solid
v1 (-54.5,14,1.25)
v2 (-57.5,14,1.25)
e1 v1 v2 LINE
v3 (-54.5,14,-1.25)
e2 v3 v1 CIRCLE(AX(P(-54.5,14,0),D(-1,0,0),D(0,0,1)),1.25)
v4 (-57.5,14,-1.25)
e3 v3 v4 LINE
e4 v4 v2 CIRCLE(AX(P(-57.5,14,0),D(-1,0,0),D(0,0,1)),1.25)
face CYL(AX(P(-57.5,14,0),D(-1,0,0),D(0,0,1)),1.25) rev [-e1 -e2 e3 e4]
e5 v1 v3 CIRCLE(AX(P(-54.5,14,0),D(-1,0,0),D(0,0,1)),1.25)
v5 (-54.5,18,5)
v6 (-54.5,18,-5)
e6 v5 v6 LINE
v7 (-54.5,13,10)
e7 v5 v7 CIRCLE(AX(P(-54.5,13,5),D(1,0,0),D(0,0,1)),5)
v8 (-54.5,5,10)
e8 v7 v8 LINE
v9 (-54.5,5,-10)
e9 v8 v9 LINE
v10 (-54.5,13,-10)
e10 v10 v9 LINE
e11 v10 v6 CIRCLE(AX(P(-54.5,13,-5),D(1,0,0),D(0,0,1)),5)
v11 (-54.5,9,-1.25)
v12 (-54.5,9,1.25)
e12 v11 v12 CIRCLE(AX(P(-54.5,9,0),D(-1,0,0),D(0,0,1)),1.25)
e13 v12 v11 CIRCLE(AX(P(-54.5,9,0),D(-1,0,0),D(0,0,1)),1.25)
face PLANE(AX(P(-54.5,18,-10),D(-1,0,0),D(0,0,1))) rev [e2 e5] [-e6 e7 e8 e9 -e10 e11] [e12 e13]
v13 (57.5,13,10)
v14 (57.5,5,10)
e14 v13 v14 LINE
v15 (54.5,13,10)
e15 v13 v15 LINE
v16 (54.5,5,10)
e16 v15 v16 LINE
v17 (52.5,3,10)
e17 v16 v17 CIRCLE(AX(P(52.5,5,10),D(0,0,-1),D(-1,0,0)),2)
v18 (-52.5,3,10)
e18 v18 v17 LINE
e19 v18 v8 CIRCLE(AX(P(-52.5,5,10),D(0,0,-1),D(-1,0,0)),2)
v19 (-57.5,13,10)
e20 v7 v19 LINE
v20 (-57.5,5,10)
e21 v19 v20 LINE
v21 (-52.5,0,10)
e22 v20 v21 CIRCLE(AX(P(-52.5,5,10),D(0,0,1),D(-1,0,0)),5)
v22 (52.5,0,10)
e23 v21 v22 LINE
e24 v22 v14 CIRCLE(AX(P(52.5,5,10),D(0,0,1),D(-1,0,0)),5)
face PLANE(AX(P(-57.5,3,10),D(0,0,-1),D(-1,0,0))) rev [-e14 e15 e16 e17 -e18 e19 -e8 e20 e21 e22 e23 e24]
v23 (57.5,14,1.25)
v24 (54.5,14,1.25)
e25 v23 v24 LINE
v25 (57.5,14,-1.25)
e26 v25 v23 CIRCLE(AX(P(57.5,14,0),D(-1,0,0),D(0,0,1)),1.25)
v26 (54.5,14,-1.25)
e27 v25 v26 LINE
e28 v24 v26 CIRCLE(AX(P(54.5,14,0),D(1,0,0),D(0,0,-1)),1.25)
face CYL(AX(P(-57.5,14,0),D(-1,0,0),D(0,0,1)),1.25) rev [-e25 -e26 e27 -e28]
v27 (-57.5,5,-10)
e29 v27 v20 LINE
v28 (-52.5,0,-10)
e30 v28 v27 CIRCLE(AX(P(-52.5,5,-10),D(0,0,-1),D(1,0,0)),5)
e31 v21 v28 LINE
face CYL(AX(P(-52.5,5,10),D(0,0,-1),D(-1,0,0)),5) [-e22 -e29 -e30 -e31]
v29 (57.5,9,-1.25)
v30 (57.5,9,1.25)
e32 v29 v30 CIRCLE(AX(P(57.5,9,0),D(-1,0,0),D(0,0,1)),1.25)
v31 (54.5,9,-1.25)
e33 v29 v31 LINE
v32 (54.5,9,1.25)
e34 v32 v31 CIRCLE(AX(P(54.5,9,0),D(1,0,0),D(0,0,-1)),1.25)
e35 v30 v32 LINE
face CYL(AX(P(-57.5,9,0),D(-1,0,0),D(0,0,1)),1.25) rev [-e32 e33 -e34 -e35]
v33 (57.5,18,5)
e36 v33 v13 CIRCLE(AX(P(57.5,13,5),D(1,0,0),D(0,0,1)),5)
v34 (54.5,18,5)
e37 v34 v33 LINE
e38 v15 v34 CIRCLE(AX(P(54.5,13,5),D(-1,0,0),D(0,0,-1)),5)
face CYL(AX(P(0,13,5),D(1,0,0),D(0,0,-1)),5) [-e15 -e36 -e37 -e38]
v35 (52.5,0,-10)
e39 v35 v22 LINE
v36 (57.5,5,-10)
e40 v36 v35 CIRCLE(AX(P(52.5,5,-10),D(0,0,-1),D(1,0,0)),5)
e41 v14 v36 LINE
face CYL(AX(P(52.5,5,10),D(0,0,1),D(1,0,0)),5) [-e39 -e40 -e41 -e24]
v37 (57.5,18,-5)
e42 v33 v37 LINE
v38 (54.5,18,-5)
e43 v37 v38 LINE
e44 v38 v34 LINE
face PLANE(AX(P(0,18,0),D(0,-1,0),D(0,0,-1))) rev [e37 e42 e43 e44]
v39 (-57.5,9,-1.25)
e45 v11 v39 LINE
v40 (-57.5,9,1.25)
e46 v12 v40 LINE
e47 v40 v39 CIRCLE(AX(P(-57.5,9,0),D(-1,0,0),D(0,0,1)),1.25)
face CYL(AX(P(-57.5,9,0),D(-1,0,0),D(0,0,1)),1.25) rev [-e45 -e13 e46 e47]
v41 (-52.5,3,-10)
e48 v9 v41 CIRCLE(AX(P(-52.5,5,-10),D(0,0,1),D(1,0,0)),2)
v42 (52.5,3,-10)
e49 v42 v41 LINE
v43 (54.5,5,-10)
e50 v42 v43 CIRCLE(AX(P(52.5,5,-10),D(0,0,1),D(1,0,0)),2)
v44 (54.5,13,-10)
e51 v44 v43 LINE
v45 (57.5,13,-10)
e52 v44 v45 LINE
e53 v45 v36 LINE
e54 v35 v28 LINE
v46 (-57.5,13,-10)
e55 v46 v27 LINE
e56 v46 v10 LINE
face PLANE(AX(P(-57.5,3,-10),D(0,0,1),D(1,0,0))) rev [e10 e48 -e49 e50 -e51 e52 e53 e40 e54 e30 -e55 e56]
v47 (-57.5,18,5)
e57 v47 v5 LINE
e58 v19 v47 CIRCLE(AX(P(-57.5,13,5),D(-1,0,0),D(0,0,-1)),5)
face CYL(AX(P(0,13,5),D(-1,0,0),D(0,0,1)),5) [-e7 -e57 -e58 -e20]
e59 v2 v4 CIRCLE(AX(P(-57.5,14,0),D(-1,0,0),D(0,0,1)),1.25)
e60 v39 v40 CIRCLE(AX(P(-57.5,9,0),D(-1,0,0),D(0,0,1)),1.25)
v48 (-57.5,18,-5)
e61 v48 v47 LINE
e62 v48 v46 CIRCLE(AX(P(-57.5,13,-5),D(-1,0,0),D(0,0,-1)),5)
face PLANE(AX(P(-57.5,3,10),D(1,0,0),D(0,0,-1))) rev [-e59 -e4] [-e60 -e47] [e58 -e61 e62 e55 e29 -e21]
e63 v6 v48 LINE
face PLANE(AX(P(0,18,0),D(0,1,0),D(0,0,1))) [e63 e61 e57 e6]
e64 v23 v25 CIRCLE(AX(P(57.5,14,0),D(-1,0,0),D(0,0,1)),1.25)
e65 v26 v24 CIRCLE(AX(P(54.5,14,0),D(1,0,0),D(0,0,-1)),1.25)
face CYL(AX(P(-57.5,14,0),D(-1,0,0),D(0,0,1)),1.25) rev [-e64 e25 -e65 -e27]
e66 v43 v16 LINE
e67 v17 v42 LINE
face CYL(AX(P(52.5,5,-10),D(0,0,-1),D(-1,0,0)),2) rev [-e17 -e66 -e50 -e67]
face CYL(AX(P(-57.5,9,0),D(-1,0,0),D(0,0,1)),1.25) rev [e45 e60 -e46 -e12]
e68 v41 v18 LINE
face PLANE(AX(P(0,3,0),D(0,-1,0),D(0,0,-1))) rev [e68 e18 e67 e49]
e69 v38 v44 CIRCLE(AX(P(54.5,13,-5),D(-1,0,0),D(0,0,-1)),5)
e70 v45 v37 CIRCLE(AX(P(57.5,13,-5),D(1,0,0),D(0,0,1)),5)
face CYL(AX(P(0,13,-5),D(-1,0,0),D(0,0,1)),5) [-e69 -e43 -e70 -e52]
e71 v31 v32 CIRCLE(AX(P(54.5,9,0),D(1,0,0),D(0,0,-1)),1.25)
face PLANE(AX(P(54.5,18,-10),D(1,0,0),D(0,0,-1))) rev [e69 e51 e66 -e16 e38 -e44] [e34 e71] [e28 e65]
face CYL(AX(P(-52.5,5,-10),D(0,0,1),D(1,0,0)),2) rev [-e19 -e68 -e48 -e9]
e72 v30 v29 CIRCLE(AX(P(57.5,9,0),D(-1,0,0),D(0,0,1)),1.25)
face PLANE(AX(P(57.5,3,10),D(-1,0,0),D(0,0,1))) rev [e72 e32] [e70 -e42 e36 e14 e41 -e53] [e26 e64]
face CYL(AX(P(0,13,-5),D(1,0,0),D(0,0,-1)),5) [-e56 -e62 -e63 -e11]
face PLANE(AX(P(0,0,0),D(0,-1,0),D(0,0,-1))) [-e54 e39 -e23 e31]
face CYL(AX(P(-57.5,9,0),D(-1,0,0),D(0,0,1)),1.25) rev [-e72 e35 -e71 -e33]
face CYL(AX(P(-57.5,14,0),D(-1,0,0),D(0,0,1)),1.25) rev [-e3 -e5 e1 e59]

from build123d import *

# Parameters (mm, degrees)
SKETCH1_W           = 115
SKETCH1_H           = 20
BOSS_EXTRUDE1_DEPTH = 3
SKETCH2_W           = 3
SKETCH2_H           = 20
BOSS_EXTRUDE2_DEPTH = 15
FILLET1_R           = 2
FILLET2_R           = 5
M3_TAPPED_HOLE1_D   = 2.5
FILLET3_R           = 5


with BuildPart() as part:
    # Sketch1 → Boss-Extrude1 (new body)
    with BuildSketch(Plane(origin=(0, 0, 0), x_dir=(1, 0, 0), z_dir=(0, 1, 0))):
        Rectangle(SKETCH1_W, SKETCH1_H)
    extrude(amount=BOSS_EXTRUDE1_DEPTH)

    # Sketch2 → Boss-Extrude2 (add)
    with BuildSketch(Plane(origin=(0, 3, 0), x_dir=(1, 0, 0), z_dir=(0, 1, 0))):
        with Locations((-56, 0)):
            Rectangle(SKETCH2_W, SKETCH2_H)
        with Locations((56, 0)):
            Rectangle(SKETCH2_W, SKETCH2_H)
    extrude(amount=BOSS_EXTRUDE2_DEPTH)

    # Fillet1
    fillet1_edges = [part.edges().sort_by_distance(p)[0] for p in [
        (-54.5, 3, 0),
        (54.5, 3, 0),
    ]]
    fillet(fillet1_edges, radius=FILLET1_R)

    # Fillet2
    fillet2_edges = [part.edges().sort_by_distance(p)[0] for p in [
        (-57.5, 0, 0),
        (57.5, 0, 0),
    ]]
    fillet(fillet2_edges, radius=FILLET2_R)

    # M3 Tapped Hole1 (through all)
    with Locations(Plane.ZY.offset(57.5)):
        with Locations((0, 14), (0, 9)):
            Hole(M3_TAPPED_HOLE1_D / 2)

    # Fillet3
    fillet3_edges = [part.edges().sort_by_distance(p)[0] for p in [
        (-56, 18, 10),
        (-56, 18, -10),
        (56, 18, -10),
        (56, 18, 10),
    ]]
    fillet(fillet3_edges, radius=FILLET3_R)


solid = part.part
